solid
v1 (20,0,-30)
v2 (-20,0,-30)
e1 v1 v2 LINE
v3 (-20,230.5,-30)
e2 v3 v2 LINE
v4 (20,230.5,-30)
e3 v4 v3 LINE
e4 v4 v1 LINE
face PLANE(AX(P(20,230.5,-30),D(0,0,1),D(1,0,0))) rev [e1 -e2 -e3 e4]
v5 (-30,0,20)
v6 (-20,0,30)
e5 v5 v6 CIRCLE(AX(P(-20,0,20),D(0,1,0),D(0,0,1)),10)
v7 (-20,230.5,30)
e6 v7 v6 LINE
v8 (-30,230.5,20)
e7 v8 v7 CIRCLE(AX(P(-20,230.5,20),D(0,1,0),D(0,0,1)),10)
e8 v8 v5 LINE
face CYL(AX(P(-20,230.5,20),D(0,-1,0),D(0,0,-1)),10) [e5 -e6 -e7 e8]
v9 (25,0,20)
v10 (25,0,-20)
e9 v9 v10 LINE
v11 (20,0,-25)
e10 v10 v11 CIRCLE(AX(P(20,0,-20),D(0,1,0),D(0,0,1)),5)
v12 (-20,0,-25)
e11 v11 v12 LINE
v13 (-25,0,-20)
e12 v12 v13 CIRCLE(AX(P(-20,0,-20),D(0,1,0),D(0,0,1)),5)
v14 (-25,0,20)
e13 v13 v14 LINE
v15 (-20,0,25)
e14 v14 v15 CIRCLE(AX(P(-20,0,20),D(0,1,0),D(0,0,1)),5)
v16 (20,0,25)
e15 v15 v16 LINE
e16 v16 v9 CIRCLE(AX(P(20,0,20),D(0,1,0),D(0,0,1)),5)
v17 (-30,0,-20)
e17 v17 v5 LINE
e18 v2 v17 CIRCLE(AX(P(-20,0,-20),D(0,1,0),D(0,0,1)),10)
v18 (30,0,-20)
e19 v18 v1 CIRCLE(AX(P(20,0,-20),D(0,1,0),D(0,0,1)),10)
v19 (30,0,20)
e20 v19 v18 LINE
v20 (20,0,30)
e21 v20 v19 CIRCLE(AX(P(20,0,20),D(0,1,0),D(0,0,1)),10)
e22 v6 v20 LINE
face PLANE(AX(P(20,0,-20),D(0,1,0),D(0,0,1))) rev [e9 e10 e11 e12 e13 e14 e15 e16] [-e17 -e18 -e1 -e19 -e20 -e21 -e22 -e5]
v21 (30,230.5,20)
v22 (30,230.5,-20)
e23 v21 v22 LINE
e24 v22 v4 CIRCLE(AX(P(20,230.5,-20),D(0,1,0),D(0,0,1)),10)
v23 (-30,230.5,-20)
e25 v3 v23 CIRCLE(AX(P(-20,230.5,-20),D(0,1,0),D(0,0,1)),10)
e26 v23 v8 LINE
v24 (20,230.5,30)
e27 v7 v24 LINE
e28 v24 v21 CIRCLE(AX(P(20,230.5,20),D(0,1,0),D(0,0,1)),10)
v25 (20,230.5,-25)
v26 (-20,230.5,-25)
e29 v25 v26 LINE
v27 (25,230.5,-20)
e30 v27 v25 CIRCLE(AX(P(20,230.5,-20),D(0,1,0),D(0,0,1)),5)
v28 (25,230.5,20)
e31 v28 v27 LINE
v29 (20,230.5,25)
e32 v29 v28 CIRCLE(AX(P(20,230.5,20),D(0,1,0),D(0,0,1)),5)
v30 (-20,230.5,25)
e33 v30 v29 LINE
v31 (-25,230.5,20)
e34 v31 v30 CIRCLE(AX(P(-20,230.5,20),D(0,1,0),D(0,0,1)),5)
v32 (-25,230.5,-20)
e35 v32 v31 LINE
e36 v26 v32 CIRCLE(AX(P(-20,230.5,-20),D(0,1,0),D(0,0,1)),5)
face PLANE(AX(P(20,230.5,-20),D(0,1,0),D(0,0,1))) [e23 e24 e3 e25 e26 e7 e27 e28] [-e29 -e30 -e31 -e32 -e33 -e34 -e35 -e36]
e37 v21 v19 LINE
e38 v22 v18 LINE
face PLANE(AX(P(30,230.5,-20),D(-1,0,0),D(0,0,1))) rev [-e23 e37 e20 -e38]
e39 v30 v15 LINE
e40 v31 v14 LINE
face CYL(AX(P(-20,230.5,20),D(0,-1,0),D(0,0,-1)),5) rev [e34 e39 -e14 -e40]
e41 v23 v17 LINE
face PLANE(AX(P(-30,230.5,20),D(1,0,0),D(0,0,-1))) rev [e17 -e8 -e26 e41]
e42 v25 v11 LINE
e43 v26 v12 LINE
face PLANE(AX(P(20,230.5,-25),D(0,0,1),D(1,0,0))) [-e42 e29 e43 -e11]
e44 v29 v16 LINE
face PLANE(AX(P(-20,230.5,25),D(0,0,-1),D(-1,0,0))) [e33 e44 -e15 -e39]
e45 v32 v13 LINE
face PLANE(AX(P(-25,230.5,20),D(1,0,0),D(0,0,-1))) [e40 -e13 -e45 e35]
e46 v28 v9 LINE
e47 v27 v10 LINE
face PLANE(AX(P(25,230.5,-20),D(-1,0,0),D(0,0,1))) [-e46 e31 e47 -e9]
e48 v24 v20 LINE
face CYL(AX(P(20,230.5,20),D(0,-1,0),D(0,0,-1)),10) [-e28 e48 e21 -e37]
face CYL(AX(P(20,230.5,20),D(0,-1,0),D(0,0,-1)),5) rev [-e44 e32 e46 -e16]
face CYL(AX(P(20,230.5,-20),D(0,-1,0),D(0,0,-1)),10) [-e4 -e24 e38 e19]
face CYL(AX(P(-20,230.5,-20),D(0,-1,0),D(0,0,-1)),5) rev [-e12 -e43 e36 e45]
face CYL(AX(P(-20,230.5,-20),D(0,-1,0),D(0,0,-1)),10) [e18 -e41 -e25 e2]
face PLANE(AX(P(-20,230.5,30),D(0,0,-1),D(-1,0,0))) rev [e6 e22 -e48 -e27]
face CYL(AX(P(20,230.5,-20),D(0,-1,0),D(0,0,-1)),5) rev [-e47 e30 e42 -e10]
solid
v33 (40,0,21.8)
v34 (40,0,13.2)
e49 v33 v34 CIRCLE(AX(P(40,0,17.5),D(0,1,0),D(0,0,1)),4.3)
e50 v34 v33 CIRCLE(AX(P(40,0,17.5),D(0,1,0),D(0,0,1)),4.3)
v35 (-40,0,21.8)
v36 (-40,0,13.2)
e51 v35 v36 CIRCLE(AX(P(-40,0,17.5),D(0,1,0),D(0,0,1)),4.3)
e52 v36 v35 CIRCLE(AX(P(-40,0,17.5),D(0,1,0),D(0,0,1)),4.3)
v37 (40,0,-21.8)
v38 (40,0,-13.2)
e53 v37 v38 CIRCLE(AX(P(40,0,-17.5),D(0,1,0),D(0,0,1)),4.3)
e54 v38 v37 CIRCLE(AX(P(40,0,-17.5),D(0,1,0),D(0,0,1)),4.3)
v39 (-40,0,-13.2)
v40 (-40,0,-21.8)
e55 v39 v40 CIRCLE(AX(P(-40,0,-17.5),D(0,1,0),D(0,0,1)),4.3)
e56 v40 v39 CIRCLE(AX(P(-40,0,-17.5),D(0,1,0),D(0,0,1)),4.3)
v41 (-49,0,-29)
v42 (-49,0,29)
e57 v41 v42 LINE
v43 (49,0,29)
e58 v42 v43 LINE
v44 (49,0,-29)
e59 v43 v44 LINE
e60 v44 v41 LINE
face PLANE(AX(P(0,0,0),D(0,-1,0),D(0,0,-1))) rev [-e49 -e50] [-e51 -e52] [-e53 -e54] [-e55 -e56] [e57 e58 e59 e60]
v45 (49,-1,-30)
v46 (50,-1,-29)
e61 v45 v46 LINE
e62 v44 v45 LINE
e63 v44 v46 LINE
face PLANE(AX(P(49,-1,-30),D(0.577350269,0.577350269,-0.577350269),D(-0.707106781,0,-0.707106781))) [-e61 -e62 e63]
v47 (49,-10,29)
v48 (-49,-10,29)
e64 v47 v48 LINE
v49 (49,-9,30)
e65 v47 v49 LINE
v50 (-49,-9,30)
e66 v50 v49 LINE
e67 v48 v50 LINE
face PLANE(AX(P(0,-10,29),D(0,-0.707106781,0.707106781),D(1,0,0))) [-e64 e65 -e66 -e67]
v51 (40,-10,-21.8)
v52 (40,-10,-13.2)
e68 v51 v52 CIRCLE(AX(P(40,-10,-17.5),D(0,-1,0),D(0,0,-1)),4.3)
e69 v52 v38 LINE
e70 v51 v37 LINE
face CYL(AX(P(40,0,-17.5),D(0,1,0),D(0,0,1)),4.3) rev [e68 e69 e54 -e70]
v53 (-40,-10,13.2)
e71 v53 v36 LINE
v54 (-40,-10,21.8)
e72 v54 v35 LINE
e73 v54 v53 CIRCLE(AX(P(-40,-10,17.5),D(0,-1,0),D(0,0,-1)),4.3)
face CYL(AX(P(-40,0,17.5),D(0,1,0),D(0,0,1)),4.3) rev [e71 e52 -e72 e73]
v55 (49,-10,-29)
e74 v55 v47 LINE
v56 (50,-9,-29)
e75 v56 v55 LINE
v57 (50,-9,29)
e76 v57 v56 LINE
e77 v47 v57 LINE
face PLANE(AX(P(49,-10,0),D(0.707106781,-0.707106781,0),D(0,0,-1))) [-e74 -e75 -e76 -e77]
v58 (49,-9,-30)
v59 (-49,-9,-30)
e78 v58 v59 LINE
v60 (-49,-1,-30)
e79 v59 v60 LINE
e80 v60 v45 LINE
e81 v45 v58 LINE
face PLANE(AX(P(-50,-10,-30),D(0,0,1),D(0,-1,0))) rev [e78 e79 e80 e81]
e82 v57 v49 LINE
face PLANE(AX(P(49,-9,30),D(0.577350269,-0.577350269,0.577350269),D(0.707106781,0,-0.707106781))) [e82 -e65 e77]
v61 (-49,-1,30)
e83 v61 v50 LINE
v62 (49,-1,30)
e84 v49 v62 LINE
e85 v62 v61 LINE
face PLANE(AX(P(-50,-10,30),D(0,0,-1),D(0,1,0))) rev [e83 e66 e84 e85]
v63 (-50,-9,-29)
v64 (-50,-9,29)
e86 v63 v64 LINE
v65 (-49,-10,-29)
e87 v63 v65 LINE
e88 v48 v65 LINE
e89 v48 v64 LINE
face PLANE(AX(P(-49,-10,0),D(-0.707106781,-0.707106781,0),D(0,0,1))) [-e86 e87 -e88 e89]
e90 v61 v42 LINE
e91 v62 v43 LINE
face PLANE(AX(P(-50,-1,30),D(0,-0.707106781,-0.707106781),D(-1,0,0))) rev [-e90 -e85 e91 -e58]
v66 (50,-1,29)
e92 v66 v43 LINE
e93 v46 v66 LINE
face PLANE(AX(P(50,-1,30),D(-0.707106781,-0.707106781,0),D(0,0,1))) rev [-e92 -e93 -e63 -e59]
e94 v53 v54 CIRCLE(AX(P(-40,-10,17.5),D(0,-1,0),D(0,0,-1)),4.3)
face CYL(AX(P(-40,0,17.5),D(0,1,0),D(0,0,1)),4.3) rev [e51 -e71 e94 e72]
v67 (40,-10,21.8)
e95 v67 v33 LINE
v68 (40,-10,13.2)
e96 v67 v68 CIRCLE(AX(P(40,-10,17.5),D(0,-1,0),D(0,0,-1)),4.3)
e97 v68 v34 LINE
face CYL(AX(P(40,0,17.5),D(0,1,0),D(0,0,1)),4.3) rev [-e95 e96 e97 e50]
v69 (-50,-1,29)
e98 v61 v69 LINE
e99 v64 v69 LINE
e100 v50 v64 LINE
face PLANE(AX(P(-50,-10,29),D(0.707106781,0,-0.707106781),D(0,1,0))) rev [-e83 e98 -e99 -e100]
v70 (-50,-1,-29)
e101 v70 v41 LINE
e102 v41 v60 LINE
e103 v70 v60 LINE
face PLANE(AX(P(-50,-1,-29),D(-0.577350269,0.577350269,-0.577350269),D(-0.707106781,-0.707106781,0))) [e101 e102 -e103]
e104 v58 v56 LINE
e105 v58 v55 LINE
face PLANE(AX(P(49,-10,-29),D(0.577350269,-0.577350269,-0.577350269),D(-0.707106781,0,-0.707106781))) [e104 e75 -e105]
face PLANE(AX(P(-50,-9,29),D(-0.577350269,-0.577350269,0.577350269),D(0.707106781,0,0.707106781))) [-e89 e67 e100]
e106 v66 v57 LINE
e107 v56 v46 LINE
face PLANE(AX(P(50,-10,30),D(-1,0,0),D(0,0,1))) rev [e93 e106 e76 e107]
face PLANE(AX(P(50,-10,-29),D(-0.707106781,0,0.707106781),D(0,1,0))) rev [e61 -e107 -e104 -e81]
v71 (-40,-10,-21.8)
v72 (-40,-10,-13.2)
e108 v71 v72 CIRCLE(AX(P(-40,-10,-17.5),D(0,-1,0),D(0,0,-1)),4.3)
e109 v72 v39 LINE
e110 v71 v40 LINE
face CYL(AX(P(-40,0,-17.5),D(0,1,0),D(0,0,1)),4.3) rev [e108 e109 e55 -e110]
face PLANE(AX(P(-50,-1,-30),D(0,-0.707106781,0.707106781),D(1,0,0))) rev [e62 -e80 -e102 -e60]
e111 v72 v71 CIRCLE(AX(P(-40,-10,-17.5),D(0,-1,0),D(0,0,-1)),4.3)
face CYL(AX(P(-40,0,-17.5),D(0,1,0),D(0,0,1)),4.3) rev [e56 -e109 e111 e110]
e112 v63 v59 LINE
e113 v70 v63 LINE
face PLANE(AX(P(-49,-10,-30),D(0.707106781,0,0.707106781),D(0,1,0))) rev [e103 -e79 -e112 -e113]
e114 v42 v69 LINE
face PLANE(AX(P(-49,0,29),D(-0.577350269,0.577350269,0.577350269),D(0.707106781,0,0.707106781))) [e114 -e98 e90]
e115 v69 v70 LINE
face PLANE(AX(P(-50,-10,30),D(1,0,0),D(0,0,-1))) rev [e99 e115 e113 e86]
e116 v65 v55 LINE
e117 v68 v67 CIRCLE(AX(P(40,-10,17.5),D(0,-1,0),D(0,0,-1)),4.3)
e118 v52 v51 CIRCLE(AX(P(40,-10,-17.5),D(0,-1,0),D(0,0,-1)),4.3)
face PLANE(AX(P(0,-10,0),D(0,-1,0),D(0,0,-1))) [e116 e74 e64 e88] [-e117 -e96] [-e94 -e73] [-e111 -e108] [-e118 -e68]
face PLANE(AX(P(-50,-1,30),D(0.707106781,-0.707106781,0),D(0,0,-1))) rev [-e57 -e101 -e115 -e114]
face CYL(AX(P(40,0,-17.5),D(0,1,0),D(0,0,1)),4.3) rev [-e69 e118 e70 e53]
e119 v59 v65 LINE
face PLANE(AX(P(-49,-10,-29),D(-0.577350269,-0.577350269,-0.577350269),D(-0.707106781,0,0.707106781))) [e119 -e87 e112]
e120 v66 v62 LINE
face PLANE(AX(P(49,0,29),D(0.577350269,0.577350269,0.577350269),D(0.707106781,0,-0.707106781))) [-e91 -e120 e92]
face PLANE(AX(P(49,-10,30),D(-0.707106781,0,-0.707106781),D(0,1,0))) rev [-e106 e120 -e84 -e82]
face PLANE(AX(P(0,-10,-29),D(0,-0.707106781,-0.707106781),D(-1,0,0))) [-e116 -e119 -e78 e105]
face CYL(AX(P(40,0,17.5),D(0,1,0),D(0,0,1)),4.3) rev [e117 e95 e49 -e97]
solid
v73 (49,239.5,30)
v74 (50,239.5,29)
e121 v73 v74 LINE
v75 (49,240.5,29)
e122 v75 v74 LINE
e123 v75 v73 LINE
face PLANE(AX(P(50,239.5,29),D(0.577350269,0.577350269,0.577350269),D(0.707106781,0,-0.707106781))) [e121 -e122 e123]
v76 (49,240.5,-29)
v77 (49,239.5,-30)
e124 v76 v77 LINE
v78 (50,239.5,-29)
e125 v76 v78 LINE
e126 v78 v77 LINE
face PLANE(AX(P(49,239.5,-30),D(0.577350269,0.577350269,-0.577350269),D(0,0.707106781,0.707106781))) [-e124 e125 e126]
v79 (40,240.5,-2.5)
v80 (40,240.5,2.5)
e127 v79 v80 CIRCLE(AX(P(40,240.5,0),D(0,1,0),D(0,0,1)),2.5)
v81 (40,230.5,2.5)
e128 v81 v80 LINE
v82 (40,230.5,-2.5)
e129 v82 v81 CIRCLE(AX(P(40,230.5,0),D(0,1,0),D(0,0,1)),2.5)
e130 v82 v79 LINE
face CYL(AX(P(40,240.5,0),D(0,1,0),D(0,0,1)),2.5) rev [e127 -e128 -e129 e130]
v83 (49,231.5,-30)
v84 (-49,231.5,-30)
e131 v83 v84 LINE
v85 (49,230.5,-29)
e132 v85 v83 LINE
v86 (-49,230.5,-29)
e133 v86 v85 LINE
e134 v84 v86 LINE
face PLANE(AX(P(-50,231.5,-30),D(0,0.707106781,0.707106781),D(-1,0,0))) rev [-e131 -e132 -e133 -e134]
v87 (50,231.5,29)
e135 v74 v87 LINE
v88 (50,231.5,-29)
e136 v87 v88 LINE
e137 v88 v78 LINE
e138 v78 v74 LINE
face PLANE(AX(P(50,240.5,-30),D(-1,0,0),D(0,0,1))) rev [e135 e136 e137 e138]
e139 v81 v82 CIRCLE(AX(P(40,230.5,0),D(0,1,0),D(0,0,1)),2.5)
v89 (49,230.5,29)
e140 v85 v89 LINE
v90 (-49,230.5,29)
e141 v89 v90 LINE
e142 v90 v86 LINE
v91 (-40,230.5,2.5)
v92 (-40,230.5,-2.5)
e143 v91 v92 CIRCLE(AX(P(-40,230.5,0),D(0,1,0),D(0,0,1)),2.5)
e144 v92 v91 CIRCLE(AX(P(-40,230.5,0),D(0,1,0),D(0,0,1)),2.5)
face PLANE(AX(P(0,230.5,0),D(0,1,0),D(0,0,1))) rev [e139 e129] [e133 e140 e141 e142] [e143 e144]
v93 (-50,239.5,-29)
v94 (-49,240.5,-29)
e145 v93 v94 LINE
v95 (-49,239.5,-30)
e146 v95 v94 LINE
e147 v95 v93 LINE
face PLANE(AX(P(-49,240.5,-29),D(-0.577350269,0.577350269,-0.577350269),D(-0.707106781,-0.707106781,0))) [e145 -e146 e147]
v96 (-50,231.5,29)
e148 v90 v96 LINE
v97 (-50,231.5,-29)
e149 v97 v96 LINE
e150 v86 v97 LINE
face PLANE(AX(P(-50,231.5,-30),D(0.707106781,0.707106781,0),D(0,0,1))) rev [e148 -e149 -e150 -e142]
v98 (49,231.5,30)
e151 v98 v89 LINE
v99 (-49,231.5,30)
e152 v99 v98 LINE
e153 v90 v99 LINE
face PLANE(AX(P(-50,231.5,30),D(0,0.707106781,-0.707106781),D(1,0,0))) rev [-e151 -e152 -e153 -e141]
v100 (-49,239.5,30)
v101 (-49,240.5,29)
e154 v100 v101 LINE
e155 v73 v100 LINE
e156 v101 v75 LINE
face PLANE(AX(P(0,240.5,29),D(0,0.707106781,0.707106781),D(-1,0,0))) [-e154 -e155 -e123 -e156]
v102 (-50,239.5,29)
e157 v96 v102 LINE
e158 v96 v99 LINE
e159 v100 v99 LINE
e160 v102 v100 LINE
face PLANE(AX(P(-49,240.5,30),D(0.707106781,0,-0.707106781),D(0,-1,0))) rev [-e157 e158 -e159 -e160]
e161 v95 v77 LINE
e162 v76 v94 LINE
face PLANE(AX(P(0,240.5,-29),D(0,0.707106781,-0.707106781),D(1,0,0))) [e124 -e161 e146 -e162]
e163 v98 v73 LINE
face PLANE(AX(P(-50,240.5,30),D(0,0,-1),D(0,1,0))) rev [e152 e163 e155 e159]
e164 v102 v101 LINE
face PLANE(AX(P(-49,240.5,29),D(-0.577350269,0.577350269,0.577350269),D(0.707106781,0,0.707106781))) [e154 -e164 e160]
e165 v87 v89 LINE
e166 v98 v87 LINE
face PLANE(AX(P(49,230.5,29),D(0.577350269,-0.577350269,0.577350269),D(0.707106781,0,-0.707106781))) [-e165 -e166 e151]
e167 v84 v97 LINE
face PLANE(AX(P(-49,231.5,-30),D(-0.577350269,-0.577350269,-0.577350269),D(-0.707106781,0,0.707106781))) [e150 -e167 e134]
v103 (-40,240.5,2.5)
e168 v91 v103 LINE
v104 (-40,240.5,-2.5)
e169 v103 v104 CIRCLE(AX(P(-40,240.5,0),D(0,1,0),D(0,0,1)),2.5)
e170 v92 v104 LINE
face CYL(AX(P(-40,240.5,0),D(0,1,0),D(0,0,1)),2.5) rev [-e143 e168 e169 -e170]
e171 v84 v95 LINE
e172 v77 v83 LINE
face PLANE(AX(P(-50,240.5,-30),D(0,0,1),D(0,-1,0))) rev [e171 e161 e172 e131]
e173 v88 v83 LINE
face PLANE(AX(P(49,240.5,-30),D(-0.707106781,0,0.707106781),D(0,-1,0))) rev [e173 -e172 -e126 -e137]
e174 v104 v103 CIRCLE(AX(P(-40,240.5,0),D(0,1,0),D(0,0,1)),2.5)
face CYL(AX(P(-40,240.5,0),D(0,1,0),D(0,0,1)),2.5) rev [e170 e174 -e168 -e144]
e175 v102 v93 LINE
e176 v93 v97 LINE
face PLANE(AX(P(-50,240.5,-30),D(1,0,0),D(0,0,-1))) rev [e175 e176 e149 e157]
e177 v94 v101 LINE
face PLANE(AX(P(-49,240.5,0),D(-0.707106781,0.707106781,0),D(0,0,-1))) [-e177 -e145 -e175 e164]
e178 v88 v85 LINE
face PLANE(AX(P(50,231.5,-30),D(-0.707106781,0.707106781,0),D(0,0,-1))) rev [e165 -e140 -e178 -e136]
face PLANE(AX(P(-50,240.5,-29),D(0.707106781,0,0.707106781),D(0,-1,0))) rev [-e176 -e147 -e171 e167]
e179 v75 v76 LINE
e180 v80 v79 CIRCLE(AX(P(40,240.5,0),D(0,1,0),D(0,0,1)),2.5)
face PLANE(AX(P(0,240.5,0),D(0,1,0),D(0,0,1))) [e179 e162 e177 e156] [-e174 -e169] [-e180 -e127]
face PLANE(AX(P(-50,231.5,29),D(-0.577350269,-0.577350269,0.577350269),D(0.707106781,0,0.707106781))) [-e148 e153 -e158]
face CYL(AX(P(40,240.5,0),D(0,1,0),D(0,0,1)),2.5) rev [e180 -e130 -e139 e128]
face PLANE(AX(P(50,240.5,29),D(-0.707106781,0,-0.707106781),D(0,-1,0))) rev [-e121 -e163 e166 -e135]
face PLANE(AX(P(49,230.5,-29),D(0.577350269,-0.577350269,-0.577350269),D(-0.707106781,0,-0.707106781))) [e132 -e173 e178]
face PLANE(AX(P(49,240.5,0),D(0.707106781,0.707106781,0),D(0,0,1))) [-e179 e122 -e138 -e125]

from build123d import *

# Parameters (mm, degrees)
MEMBER_1_DEPTH                   = 230.5
SKETCH_2_W                       = 100
SKETCH_2_H                       = 60
EXTRUDE_1_DEPTH                  = 10
SKETCH_3_W                       = 100
SKETCH_3_H                       = 60
EXTRUDE_2_DEPTH                  = 10
CHAMFER_1_SIZE                   = 1
CHAMFER_2_SIZE                   = 1
HOLE_WIZARD_8_6_8_6_1_AT_2_COUNT = 2
HOLE_WIZARD_8_6_8_6_1_AT_2_PITCH = 35
HOLE_WIZARD_8_6_8_6_1_AT_3_COUNT = 2
HOLE_WIZARD_8_6_8_6_1_AT_3_PITCH = 80
HOLE_WIZARD_8_6_8_6_1_AT_4_COUNT = 2
HOLE_WIZARD_8_6_8_6_1_AT_4_PITCH = 87.321245983
HOLE_WIZARD_M6_1_AT_2_COUNT      = 2
HOLE_WIZARD_M6_1_AT_2_PITCH      = 80


with BuildPart() as part:
    # Sketch11 → Member 1 (new body)
    with BuildSketch(Plane(origin=(0, 0, 0), x_dir=(1, 0, 0), z_dir=(0, 1, 0))):
        with BuildLine():
            Line((-20, -30), (20, -30))
            ThreePointArc((20, -30), (27.071067812, -27.071067812), (30, -20))
            Line((30, -20), (30, 20))
            ThreePointArc((30, 20), (27.071067812, 27.071067812), (20, 30))
            Line((20, 30), (-20, 30))
            ThreePointArc((-20, 30), (-27.071067812, 27.071067812), (-30, 20))
            Line((-30, 20), (-30, -20))
            ThreePointArc((-30, -20), (-27.071067812, -27.071067812), (-20, -30))
        make_face()
        with BuildLine():
            Line((-20, -25), (20, -25))
            ThreePointArc((20, -25), (23.535533906, -23.535533906), (25, -20))
            Line((25, -20), (25, 20))
            ThreePointArc((25, 20), (23.535533906, 23.535533906), (20, 25))
            Line((20, 25), (-20, 25))
            ThreePointArc((-20, 25), (-23.535533906, 23.535533906), (-25, 20))
            Line((-25, 20), (-25, -20))
            ThreePointArc((-25, -20), (-23.535533906, -23.535533906), (-20, -25))
        make_face(mode=Mode.SUBTRACT)
    extrude(amount=MEMBER_1_DEPTH)


with BuildPart() as body_2:
    # 草图2 → 凸台-拉伸1 (new body)
    with BuildSketch(Plane(origin=(0, 230.5, 0), x_dir=(1, 0, 0), z_dir=(0, 1, 0))):
        Rectangle(SKETCH_2_W, SKETCH_2_H)
    extrude(amount=EXTRUDE_1_DEPTH)

    # 倒角1
    chamfer_1_edges = [body_2.edges().sort_by_distance(p)[0] for p in [
        (-50, 240.5, 0),
        (0, 240.5, 30),
        (50, 240.5, 0),
        (0, 230.5, 30),
        (-50, 230.5, 0),
        (0, 230.5, -30),
        (50, 230.5, 0),
        (0, 240.5, -30),
        (50, 235.5, 30),
        (-50, 235.5, 30),
        (-50, 235.5, -30),
        (50, 235.5, -30),
    ]]
    chamfer(chamfer_1_edges, length=CHAMFER_1_SIZE)

    # 草图11 → M6 螺纹孔1 (revolve, cut)
    with BuildSketch(Plane(origin=(-40, 240.5, 0), x_dir=(0, 0, 1), z_dir=(1, 0, 0))):
        Polygon((0, 0), (0, 18.502151548), (2.5, 17), (2.5, 0), align=None)
    hole_wizard_m6_1 = revolve(axis=Axis((-40, 246.85, 0), (0, -1, 0)), mode=Mode.SUBTRACT)

    # M6 螺纹孔1 at 2: M6 螺纹孔1 ×2
    with Locations(*[(i * HOLE_WIZARD_M6_1_AT_2_PITCH, 0, 0) for i in range(1, HOLE_WIZARD_M6_1_AT_2_COUNT)]):
        add(hole_wizard_m6_1, mode=Mode.SUBTRACT)


with BuildPart() as body_3:
    # 草图3 → 凸台-拉伸2 (new body)
    with BuildSketch(Plane.XZ):
        Rectangle(SKETCH_3_W, SKETCH_3_H)
    extrude(amount=EXTRUDE_2_DEPTH)

    # 倒角2
    chamfer_2_edges = [body_3.edges().sort_by_distance(p)[0] for p in [
        (-50, -10, 0),
        (0, -10, -30),
        (50, -10, 0),
        (0, 0, -30),
        (-50, 0, 0),
        (0, 0, 30),
        (50, 0, 0),
        (0, -10, 30),
        (50, -5, -30),
        (-50, -5, -30),
        (-50, -5, 30),
        (50, -5, 30),
    ]]
    chamfer(chamfer_2_edges, length=CHAMFER_2_SIZE)

    # 草图4 → Ø8.6 (8.6) 直径孔1 (revolve, cut)
    with BuildSketch(Plane(origin=(40, 0, -17.5), x_dir=(0, 0, 1), z_dir=(1, 0, 0))):
        Polygon((0, 0), (0, 18.092606158), (4.3, 15.61), (4.3, 0), align=None)
    hole_wizard_8_6_8_6_1 = revolve(axis=Axis((40, 6.35, -17.5), (0, -1, 0)), mode=Mode.SUBTRACT)

    # Ø8.6 (8.6) 直径孔1 at 2: Ø8.6 (8.6) 直径孔1 ×2
    with Locations(*[(0, 0, i * HOLE_WIZARD_8_6_8_6_1_AT_2_PITCH) for i in range(1, HOLE_WIZARD_8_6_8_6_1_AT_2_COUNT)]):
        add(hole_wizard_8_6_8_6_1, mode=Mode.SUBTRACT)

    # Ø8.6 (8.6) 直径孔1 at 3: Ø8.6 (8.6) 直径孔1 ×2
    with Locations(*[(-i * HOLE_WIZARD_8_6_8_6_1_AT_3_PITCH, 0, 0) for i in range(1, HOLE_WIZARD_8_6_8_6_1_AT_3_COUNT)]):
        add(hole_wizard_8_6_8_6_1, mode=Mode.SUBTRACT)

    # Ø8.6 (8.6) 直径孔1 at 4: Ø8.6 (8.6) 直径孔1 ×2
    with Locations(*[Vector(-0.9161573349021891, 0, 0.4008188340197079) * (i * HOLE_WIZARD_8_6_8_6_1_AT_4_PITCH) for i in range(1, HOLE_WIZARD_8_6_8_6_1_AT_4_COUNT)]):
        add(hole_wizard_8_6_8_6_1, mode=Mode.SUBTRACT)


solid = Compound([part.part, body_2.part, body_3.part])
